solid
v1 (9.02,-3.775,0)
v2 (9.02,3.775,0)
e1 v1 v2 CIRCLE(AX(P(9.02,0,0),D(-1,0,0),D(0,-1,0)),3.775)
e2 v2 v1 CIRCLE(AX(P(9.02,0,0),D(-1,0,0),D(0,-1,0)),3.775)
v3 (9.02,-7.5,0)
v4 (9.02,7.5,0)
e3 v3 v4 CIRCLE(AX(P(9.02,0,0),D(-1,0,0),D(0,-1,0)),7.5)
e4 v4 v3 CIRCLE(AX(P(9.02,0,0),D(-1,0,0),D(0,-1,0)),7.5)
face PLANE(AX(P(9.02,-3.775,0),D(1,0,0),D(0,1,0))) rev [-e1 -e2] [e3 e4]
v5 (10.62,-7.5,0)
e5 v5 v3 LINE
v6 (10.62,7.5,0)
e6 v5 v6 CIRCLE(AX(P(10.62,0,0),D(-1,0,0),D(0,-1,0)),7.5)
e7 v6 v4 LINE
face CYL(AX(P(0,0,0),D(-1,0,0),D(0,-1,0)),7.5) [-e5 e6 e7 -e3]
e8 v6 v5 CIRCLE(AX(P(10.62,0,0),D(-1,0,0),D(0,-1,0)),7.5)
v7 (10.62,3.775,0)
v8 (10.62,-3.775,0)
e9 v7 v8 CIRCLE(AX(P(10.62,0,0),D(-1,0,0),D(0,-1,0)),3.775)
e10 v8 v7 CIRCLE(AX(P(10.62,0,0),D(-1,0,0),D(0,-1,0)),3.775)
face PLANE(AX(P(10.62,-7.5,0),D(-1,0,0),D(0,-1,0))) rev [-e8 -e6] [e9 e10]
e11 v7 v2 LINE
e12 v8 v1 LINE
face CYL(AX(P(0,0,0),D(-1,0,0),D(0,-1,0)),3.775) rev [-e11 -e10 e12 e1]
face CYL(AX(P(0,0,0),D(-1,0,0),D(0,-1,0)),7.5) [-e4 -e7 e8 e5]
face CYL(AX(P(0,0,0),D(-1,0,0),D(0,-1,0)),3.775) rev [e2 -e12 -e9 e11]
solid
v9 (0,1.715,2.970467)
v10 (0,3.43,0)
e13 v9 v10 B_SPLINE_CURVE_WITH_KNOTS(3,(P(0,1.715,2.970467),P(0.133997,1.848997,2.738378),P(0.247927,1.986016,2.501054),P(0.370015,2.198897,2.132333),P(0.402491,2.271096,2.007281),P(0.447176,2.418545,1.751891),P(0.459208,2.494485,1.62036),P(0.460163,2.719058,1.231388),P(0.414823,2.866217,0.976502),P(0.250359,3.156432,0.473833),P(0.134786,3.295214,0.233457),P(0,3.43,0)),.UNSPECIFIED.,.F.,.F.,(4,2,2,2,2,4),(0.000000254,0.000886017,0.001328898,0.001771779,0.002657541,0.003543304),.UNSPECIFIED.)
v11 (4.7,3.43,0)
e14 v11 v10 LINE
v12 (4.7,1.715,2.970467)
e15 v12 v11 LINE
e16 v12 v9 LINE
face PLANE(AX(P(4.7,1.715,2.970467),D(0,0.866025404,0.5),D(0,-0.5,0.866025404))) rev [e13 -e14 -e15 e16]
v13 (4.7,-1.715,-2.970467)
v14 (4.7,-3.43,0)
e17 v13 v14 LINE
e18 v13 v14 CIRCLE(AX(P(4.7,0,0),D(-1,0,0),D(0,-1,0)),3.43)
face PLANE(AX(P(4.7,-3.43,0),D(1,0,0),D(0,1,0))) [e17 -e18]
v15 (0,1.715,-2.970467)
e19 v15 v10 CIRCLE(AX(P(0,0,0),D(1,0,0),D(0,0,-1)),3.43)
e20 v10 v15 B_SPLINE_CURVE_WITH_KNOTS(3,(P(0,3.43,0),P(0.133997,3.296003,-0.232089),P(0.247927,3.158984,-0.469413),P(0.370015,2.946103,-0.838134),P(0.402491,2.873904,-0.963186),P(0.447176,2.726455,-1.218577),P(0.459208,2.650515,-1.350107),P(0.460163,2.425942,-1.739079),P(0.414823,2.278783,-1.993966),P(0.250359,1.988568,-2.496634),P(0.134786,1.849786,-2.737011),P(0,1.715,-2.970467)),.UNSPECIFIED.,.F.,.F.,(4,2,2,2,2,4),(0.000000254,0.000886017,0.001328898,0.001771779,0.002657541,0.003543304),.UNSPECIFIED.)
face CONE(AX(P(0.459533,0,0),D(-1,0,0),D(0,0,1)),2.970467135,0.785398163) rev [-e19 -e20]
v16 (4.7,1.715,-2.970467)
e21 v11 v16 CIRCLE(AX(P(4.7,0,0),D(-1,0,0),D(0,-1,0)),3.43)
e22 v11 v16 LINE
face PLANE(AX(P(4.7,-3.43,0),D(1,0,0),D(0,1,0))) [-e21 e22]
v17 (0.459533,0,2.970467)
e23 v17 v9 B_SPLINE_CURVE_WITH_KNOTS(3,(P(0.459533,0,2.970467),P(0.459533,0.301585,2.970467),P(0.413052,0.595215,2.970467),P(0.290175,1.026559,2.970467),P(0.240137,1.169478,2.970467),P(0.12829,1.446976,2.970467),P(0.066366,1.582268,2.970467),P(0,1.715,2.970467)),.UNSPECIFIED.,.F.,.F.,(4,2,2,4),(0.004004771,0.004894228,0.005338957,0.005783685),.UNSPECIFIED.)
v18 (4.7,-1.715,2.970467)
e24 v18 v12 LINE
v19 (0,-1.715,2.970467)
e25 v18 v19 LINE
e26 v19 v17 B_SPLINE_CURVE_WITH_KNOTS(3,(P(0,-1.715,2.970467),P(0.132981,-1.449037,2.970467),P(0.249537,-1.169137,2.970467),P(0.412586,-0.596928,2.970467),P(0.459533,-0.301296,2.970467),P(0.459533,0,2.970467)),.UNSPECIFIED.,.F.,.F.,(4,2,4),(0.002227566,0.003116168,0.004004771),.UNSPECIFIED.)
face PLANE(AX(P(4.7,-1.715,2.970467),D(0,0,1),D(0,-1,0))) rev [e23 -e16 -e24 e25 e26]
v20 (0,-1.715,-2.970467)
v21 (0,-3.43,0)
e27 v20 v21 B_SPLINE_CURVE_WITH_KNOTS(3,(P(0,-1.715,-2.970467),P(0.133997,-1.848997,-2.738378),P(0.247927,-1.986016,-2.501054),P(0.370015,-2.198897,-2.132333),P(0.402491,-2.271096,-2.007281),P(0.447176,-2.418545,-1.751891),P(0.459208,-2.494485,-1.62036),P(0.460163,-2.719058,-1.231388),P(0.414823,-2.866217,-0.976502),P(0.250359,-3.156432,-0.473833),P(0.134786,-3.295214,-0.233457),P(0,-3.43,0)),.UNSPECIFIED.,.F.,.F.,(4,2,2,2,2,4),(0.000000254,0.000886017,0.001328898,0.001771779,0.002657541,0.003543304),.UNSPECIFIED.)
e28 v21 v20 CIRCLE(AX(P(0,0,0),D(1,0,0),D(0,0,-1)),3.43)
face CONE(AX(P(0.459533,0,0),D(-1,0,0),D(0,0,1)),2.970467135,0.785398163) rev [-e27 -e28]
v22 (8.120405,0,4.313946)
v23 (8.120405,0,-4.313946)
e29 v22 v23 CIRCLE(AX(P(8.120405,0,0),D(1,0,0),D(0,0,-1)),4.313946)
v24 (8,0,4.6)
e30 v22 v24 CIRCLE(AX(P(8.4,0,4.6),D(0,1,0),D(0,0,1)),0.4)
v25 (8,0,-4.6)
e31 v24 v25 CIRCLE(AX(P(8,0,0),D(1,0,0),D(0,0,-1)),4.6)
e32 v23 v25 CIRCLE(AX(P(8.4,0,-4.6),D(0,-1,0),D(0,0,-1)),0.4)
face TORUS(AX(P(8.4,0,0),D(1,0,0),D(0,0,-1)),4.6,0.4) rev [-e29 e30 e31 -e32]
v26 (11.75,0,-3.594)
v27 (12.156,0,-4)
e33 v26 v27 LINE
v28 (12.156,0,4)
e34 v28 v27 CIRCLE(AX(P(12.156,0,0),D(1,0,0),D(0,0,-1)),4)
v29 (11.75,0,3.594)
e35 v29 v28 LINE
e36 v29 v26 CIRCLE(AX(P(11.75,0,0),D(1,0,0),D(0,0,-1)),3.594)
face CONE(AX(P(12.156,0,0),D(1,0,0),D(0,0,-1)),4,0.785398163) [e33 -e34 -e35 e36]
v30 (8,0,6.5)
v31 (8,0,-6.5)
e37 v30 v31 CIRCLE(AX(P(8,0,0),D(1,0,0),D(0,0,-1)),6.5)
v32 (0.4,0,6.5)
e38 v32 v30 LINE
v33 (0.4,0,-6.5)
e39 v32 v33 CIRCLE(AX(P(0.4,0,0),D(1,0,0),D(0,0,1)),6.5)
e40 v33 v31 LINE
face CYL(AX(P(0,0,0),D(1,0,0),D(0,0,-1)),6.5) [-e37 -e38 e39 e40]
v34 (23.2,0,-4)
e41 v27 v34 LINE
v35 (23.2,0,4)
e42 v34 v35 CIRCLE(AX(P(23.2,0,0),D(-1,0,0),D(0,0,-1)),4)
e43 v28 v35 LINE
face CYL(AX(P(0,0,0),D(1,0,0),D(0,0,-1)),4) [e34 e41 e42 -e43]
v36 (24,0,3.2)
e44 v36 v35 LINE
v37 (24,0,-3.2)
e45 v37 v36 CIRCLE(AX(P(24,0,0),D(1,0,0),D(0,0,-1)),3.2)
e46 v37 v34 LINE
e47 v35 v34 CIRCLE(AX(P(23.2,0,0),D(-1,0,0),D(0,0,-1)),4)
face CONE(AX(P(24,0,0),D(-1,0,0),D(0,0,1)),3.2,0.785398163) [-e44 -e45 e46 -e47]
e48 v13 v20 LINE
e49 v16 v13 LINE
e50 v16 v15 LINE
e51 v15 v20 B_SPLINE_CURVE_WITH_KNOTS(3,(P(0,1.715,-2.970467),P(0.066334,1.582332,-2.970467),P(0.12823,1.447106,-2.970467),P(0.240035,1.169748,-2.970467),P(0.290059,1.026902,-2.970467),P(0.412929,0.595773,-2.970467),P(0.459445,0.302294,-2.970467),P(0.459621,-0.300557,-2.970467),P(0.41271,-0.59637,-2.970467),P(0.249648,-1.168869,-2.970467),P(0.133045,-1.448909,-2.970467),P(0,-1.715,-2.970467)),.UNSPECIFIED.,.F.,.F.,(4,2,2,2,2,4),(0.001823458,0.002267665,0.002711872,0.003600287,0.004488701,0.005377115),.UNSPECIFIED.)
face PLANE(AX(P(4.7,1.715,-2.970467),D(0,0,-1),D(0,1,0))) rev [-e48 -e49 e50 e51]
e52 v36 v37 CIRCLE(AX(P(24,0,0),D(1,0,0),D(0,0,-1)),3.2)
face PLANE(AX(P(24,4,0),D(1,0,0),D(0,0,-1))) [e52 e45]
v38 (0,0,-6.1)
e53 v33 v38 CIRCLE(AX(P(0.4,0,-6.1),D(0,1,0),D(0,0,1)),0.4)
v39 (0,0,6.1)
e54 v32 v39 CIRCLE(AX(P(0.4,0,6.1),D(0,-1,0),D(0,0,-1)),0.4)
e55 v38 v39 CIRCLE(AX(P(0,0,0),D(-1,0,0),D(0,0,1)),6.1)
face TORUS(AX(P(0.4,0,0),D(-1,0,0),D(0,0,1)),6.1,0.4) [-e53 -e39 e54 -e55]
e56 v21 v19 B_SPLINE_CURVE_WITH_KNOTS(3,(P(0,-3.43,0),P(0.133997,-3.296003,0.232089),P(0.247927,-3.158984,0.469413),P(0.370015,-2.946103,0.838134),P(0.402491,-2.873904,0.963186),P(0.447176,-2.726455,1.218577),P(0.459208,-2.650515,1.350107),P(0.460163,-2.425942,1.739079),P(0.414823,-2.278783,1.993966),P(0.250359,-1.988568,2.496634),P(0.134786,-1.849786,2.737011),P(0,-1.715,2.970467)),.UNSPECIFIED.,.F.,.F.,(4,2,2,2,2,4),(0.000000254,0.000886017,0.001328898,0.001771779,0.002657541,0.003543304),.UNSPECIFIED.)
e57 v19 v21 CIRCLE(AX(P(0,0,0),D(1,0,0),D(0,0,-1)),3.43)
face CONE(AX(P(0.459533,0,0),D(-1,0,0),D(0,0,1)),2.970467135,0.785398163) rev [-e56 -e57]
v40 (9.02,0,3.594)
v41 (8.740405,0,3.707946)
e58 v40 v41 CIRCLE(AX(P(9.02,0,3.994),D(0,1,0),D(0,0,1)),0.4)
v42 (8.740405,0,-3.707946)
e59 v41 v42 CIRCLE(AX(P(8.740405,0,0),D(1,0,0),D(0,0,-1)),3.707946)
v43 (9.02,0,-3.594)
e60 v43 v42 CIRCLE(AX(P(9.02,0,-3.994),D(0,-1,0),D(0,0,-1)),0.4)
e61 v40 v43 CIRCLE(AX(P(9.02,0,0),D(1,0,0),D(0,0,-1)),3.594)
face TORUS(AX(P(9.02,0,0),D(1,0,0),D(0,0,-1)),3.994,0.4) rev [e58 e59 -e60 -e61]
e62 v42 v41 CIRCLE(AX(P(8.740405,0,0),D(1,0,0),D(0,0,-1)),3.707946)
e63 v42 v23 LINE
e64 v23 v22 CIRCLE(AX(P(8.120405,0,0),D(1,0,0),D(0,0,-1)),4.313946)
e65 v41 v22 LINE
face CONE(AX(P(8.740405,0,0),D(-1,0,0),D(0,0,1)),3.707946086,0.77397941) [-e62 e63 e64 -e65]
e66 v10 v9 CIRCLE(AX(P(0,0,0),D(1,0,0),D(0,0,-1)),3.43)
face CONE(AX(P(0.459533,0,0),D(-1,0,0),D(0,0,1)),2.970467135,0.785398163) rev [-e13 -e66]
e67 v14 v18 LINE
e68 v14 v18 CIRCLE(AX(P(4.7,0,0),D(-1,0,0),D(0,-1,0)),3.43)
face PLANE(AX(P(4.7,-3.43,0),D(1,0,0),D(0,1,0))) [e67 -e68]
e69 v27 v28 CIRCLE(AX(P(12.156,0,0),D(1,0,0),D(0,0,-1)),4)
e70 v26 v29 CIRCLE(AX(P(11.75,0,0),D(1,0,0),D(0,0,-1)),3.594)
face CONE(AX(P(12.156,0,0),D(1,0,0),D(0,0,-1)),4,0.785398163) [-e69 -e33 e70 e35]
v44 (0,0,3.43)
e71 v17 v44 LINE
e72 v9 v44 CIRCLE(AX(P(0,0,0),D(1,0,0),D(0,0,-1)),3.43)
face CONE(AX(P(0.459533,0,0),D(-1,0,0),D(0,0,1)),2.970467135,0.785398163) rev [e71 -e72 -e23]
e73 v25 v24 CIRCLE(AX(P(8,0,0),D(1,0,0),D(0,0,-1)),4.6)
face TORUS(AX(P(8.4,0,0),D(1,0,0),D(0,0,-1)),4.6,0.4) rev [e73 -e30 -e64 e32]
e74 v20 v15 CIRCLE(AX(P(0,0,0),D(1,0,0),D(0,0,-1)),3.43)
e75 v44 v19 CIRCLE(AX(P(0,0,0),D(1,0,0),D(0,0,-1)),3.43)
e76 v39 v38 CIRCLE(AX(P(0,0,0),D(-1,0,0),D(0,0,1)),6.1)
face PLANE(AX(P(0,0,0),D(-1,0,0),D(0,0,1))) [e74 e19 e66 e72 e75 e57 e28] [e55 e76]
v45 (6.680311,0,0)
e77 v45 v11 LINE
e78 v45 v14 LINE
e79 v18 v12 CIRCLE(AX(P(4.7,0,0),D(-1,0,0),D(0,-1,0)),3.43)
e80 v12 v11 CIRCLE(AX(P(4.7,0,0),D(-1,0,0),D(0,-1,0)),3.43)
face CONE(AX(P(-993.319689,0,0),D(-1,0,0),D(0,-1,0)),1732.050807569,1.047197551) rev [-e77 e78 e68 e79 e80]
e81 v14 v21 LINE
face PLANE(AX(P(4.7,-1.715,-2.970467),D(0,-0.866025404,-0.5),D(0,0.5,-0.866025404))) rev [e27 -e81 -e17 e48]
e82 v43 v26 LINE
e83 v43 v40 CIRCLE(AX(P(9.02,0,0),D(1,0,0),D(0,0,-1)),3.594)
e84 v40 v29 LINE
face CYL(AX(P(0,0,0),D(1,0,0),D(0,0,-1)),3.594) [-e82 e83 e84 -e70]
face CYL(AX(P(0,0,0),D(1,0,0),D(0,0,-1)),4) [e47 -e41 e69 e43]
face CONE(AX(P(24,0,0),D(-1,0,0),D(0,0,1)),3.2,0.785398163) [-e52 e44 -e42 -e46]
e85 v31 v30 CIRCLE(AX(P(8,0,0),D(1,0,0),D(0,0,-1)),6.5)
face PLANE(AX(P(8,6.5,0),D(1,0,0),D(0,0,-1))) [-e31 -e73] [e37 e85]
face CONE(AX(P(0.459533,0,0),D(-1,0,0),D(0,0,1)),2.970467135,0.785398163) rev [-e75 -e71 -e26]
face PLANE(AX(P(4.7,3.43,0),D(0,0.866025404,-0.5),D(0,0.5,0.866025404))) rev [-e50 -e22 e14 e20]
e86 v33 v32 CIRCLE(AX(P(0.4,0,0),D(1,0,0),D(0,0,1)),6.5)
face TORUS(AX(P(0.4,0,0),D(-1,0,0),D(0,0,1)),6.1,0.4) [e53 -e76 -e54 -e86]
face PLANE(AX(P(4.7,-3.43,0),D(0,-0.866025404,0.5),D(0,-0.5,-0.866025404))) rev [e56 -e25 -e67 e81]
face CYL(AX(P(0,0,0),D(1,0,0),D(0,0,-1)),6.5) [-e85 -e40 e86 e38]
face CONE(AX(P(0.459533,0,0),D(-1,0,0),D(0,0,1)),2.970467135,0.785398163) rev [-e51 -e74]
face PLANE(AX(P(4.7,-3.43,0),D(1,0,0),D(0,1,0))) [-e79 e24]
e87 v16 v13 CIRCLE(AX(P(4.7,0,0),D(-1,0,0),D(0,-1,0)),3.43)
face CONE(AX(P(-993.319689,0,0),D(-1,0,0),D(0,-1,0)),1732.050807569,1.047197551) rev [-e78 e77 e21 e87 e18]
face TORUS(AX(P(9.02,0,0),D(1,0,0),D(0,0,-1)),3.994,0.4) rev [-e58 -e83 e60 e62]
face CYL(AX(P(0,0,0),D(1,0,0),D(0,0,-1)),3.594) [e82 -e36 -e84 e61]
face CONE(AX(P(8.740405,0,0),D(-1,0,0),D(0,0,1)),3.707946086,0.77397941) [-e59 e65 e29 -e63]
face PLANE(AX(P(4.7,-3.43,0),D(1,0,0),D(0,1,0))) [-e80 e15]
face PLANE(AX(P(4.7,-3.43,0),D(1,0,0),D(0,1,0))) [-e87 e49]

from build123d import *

# Parameters (mm, degrees)
CUT_EXTRUDE1_DEPTH = 4.7
FILLET1_R          = 0.4
SKETCH11_W         = 1.6
SKETCH11_H         = 3.725
CHAMFER1_SIZE      = 0.8


with BuildPart() as part:
    # Sketch1 → Base-Revolve (revolve)
    with BuildSketch(Plane.XY, mode=Mode.PRIVATE) as base_revolve_sk:
        with BuildLine():
            Line((0, 0), (0, 6.5))
            Line((0, 6.5), (8, 6.5))
            Line((8, 6.5), (8, 4.6))
            ThreePointArc((8, 4.6), (8.031328159, 4.444819223), (8.120405368, 4.313946086))
            Line((8.120405368, 4.313946086), (8.740405368, 3.707946086))
            ThreePointArc((8.740405368, 3.707946086), (8.869039021, 3.623580261), (9.02, 3.594))
            Line((9.02, 3.594), (11.75, 3.594))
            Line((11.75, 3.594), (12.156, 4))
            Line((12.156, 4), (24, 4))
            Line((24, 4), (24, 0))
            Line((24, 0), (0, 0))
        make_face()
    revolve(base_revolve_sk.sketch.rotate(Axis((0, 0, 0), (-1, 0, 0)), 90), axis=Axis((0, 0, 0), (-1, 0, 0)))

    # Sketch2 → Cut-Extrude1 (cut)
    with BuildSketch(Plane.ZY):
        Polygon((2.970467135, -1.715), (2.970467135, 1.715), (0, 3.43), (-2.970467135, 1.715), (-2.970467135, -1.715), (0, -3.43), align=None)
    extrude(amount=-CUT_EXTRUDE1_DEPTH, mode=Mode.SUBTRACT)

    # Sketch13 → Cut-Revolve4 (revolve, cut)
    with BuildSketch(Plane.XY):
        Polygon((0, 3.43), (0.459532865, 2.970467135), (0, 2.970467135), align=None)
    revolve(axis=Axis((0, 0, 0), (-1, 0, 0)), mode=Mode.SUBTRACT)

    # Sketch16 → Cut-Revolve5 (revolve, cut)
    with BuildSketch(Plane.XY, mode=Mode.PRIVATE) as cut_revolve5_sk:
        Polygon((6.680311423, 0), (4.7, 3.43), (4.7, 0), align=None)
    revolve(cut_revolve5_sk.sketch.rotate(Axis((4.7, 0, 0), (1, 0, 0)), 180), axis=Axis((4.7, 0, 0), (1, 0, 0)), mode=Mode.SUBTRACT)

    # Fillet1
    fillet1_edges = [part.edges().sort_by_distance(p)[0] for p in [
        (0, 0, 6.5),
    ]]
    fillet(fillet1_edges, radius=FILLET1_R)

    # Chamfer1
    chamfer1_edges = [part.edges().sort_by_distance(p)[0] for p in [
        (24, 0, 4),
    ]]
    chamfer(chamfer1_edges, length=CHAMFER1_SIZE)


with BuildPart() as body_2:
    # Sketch11 → Revolve1 (revolve)
    with BuildSketch(Plane.XY, mode=Mode.PRIVATE) as revolve1_sk:
        with Locations((9.82, 5.6375)):
            Rectangle(SKETCH11_W, SKETCH11_H)
    revolve(revolve1_sk.sketch.rotate(Axis((0, 0, 0), (1, 0, 0)), 180), axis=Axis((0, 0, 0), (1, 0, 0)))


solid = Compound([part.part, body_2.part])
